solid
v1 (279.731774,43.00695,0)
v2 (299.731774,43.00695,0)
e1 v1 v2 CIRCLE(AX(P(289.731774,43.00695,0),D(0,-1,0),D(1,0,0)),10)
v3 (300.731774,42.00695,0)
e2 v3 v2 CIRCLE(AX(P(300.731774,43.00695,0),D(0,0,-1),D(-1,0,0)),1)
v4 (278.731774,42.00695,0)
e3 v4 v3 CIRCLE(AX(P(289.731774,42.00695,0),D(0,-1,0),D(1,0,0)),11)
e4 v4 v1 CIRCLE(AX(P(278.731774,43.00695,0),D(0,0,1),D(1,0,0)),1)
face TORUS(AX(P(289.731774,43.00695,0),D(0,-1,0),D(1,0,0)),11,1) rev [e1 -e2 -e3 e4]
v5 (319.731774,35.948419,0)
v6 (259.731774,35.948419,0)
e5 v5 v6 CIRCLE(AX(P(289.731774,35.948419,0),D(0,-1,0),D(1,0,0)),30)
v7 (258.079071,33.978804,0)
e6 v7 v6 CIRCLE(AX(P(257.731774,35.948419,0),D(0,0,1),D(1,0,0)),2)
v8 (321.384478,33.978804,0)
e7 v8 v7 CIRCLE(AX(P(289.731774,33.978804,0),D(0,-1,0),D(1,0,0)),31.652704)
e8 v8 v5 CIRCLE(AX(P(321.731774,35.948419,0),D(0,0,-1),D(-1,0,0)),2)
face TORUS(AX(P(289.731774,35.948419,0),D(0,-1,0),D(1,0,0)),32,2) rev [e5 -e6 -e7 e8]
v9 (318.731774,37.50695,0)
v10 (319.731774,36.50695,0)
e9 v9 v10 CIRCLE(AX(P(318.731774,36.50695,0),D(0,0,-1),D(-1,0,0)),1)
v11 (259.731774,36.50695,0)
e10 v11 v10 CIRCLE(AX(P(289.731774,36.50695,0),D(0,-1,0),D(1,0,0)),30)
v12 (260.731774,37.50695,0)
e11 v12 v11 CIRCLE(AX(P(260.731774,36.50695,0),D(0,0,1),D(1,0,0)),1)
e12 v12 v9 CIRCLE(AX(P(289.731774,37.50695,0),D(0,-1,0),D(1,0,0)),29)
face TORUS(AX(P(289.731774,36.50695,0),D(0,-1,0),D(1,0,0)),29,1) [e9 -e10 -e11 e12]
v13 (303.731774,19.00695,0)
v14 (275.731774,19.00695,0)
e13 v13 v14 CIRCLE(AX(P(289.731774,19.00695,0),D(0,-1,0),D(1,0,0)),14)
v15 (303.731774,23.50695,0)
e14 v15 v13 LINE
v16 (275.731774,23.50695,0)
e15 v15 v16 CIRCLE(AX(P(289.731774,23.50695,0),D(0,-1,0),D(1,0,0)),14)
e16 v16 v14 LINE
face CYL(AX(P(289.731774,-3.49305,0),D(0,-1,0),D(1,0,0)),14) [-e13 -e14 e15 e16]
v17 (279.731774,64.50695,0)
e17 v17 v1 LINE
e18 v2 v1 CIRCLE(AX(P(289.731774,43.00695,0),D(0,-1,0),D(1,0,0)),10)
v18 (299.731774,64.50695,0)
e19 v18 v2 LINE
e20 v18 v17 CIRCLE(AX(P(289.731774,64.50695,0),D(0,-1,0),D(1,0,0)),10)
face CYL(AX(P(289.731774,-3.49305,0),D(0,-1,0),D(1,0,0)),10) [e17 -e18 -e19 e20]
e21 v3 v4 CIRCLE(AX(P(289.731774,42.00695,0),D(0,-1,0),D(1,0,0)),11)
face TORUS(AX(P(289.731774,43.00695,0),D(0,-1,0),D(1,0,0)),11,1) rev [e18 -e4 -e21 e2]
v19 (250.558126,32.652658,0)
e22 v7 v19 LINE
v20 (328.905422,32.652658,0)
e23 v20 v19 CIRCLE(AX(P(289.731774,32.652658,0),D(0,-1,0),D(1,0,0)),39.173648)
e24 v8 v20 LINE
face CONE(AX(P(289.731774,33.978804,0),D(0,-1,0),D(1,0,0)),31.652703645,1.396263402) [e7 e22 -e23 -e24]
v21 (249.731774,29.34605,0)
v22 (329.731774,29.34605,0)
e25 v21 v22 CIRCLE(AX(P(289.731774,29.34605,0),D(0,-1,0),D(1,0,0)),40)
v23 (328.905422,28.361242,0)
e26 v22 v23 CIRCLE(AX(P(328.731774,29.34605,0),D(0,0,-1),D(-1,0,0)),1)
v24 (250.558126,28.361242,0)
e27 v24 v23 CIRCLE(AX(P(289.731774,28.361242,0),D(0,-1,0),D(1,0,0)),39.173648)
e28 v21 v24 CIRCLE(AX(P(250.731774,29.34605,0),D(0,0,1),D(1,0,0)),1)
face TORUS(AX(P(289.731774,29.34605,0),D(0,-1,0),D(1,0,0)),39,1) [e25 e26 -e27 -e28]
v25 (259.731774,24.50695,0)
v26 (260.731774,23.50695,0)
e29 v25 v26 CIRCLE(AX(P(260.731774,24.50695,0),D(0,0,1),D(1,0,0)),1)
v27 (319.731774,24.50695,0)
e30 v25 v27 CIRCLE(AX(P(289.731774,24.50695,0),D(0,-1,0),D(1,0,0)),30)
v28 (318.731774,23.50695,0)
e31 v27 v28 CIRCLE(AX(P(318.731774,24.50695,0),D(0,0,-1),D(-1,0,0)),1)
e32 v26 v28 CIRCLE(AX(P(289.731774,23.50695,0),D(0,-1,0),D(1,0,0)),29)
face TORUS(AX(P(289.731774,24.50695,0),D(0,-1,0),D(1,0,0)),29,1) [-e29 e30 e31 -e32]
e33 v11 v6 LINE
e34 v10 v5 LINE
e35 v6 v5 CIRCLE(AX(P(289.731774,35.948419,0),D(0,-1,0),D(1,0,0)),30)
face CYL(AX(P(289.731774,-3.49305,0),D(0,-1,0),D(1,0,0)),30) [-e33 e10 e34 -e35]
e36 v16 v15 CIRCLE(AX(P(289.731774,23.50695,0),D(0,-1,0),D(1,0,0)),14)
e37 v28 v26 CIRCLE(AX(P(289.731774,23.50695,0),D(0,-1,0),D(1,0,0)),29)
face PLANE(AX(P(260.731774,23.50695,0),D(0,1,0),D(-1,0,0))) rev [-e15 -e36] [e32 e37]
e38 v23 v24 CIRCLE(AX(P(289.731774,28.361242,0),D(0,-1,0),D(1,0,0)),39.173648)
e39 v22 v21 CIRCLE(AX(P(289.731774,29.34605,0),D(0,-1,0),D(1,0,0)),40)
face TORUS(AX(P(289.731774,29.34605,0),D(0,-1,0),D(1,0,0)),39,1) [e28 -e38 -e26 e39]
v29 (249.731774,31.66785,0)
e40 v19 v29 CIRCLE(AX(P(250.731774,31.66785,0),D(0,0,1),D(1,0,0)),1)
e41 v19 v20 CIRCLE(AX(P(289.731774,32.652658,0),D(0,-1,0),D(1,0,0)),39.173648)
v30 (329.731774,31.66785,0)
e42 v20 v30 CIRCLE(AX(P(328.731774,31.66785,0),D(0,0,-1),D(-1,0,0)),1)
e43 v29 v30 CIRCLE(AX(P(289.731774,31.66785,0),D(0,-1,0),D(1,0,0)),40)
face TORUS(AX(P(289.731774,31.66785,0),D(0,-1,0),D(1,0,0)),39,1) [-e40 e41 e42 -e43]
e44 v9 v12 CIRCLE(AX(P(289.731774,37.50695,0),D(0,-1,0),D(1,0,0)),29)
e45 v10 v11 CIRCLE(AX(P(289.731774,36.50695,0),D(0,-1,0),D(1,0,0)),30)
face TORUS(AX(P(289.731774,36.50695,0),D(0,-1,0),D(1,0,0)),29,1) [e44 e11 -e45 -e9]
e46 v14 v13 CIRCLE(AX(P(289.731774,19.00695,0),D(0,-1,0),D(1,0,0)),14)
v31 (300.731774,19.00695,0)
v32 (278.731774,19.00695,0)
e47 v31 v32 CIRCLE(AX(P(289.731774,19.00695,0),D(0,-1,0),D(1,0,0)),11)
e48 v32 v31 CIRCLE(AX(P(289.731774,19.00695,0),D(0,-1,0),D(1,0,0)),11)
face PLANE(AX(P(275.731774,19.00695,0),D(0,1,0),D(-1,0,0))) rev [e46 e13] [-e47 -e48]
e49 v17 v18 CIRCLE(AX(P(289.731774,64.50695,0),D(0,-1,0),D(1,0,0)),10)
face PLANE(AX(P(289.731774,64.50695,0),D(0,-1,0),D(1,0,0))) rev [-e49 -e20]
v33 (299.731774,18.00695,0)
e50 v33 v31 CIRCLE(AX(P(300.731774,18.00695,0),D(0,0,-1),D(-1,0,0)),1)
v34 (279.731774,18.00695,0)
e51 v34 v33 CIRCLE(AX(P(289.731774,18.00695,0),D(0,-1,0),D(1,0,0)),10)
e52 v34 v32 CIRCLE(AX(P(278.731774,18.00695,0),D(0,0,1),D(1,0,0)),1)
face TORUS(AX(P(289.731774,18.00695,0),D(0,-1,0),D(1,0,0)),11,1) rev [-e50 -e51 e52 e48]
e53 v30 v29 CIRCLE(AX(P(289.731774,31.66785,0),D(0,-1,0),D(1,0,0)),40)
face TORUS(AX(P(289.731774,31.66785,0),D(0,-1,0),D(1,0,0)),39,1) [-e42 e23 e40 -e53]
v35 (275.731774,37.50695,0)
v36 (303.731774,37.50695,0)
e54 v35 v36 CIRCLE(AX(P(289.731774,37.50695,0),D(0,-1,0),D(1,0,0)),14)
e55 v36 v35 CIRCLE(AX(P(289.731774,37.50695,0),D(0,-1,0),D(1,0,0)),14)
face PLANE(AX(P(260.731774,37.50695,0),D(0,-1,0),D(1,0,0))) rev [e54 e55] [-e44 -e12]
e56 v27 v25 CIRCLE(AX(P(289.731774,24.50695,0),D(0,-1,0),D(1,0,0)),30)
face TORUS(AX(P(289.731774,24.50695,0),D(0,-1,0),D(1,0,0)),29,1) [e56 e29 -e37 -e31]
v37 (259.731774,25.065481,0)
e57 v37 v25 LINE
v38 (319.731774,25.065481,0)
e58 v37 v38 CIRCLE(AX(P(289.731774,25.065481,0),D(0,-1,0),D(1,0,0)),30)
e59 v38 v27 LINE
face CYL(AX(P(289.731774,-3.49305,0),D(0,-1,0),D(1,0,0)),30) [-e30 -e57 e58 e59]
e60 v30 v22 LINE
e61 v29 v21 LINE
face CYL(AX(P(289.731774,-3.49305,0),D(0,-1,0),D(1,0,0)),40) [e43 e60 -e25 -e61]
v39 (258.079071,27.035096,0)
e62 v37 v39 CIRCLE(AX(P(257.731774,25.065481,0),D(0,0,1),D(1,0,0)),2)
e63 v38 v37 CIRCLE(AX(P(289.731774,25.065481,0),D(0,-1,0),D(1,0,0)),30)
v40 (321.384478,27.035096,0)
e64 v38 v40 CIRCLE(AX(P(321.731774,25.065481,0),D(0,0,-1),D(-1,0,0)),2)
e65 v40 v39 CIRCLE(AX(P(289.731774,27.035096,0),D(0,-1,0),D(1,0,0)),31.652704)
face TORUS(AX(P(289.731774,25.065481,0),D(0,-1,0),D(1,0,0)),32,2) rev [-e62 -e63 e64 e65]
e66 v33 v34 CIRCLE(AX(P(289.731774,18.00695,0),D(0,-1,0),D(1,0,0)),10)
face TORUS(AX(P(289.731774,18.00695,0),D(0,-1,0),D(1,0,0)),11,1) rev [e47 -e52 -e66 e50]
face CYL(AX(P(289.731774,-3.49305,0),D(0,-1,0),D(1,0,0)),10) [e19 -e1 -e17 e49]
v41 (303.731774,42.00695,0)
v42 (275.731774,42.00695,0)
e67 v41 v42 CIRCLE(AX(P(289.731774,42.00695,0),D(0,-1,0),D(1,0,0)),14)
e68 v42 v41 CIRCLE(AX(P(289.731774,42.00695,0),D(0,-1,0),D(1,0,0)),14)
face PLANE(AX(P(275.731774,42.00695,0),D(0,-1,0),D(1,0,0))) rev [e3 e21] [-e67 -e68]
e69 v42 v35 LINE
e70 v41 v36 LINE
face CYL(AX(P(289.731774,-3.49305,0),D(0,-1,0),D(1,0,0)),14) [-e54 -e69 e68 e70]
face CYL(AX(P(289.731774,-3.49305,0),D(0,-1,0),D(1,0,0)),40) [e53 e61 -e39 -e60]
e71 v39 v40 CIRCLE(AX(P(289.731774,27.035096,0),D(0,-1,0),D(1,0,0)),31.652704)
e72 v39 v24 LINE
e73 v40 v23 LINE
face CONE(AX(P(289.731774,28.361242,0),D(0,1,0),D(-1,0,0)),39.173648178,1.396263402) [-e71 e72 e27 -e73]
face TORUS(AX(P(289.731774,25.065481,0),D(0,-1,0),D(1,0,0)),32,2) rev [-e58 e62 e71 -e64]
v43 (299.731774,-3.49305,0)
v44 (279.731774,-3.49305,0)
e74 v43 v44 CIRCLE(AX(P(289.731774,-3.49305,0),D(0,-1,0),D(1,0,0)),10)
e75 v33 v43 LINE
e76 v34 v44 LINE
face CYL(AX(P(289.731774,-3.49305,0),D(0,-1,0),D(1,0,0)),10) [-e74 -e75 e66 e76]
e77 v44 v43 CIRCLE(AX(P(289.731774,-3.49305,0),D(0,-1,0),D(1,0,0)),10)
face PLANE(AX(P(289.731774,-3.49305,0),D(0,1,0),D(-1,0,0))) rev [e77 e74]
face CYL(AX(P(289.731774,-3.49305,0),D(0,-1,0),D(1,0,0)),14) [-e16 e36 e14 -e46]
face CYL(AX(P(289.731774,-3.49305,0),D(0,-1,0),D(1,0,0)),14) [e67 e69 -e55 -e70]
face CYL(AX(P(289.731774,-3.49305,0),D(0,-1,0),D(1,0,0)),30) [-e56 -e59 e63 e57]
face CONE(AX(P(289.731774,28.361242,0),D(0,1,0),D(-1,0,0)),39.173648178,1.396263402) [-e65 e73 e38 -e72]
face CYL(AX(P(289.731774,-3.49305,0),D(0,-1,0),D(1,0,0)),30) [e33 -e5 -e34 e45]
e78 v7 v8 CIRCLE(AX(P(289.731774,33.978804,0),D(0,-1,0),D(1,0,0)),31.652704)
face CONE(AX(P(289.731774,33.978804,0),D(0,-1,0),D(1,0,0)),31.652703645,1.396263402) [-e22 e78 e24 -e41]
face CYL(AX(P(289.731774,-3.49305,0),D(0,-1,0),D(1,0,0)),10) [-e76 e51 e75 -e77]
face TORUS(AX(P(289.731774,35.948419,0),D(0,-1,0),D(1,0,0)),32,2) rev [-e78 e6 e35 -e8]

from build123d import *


with BuildPart() as part:
    # Sketch1 → Revolve1 (revolve)
    with BuildSketch(Plane.XY, mode=Mode.PRIVATE) as revolve1_sk:
        with BuildLine():
            Line((249.731774292, 31.667850424), (249.731774292, 29.346049686))
            ThreePointArc((249.731774292, 29.346049686), (249.965729849, 28.703262077), (250.558126114, 28.361241933))
            Line((250.558126114, 28.361241933), (258.079070647, 27.035096492))
            ThreePointArc((258.079070647, 27.035096492), (259.263863178, 26.351056205), (259.731774292, 25.065480986))
            Line((259.731774292, 25.065480986), (259.731774292, 24.506950055))
            ThreePointArc((259.731774292, 24.506950055), (260.024667511, 23.799843274), (260.731774292, 23.506950055))
            Line((260.731774292, 23.506950055), (275.731774292, 23.506950055))
            Line((275.731774292, 23.506950055), (275.731774292, 19.006950055))
            Line((275.731774292, 19.006950055), (278.731774292, 19.006950055))
            ThreePointArc((278.731774292, 19.006950055), (279.438881073, 18.714056836), (279.731774292, 18.006950055))
            Line((279.731774292, 18.006950055), (279.731774292, -3.493049945))
            Line((279.731774292, -3.493049945), (289.731774292, -3.493049945))
            Line((289.731774292, -3.493049945), (289.731774292, 64.506950055))
            Line((289.731774292, 64.506950055), (279.731774292, 64.506950055))
            Line((279.731774292, 64.506950055), (279.731774292, 43.006950055))
            ThreePointArc((279.731774292, 43.006950055), (279.438881073, 42.299843274), (278.731774292, 42.006950055))
            Line((278.731774292, 42.006950055), (275.731774292, 42.006950055))
            Line((275.731774292, 42.006950055), (275.731774292, 37.506950055))
            Line((275.731774292, 37.506950055), (260.731774292, 37.506950055))
            ThreePointArc((260.731774292, 37.506950055), (260.024667511, 37.214056836), (259.731774292, 36.506950055))
            Line((259.731774292, 36.506950055), (259.731774292, 35.948419125))
            ThreePointArc((259.731774292, 35.948419125), (259.263863178, 34.662843905), (258.079070647, 33.978803619))
            Line((258.079070647, 33.978803619), (250.558126114, 32.652658177))
            ThreePointArc((250.558126114, 32.652658177), (249.965729849, 32.310638034), (249.731774292, 31.667850424))
        make_face()
    revolve(revolve1_sk.sketch.rotate(Axis((289.731774292, -3.493049945, 0), (0, 1, 0)), 180), axis=Axis((289.731774292, -3.493049945, 0), (0, 1, 0)))


solid = part.part
